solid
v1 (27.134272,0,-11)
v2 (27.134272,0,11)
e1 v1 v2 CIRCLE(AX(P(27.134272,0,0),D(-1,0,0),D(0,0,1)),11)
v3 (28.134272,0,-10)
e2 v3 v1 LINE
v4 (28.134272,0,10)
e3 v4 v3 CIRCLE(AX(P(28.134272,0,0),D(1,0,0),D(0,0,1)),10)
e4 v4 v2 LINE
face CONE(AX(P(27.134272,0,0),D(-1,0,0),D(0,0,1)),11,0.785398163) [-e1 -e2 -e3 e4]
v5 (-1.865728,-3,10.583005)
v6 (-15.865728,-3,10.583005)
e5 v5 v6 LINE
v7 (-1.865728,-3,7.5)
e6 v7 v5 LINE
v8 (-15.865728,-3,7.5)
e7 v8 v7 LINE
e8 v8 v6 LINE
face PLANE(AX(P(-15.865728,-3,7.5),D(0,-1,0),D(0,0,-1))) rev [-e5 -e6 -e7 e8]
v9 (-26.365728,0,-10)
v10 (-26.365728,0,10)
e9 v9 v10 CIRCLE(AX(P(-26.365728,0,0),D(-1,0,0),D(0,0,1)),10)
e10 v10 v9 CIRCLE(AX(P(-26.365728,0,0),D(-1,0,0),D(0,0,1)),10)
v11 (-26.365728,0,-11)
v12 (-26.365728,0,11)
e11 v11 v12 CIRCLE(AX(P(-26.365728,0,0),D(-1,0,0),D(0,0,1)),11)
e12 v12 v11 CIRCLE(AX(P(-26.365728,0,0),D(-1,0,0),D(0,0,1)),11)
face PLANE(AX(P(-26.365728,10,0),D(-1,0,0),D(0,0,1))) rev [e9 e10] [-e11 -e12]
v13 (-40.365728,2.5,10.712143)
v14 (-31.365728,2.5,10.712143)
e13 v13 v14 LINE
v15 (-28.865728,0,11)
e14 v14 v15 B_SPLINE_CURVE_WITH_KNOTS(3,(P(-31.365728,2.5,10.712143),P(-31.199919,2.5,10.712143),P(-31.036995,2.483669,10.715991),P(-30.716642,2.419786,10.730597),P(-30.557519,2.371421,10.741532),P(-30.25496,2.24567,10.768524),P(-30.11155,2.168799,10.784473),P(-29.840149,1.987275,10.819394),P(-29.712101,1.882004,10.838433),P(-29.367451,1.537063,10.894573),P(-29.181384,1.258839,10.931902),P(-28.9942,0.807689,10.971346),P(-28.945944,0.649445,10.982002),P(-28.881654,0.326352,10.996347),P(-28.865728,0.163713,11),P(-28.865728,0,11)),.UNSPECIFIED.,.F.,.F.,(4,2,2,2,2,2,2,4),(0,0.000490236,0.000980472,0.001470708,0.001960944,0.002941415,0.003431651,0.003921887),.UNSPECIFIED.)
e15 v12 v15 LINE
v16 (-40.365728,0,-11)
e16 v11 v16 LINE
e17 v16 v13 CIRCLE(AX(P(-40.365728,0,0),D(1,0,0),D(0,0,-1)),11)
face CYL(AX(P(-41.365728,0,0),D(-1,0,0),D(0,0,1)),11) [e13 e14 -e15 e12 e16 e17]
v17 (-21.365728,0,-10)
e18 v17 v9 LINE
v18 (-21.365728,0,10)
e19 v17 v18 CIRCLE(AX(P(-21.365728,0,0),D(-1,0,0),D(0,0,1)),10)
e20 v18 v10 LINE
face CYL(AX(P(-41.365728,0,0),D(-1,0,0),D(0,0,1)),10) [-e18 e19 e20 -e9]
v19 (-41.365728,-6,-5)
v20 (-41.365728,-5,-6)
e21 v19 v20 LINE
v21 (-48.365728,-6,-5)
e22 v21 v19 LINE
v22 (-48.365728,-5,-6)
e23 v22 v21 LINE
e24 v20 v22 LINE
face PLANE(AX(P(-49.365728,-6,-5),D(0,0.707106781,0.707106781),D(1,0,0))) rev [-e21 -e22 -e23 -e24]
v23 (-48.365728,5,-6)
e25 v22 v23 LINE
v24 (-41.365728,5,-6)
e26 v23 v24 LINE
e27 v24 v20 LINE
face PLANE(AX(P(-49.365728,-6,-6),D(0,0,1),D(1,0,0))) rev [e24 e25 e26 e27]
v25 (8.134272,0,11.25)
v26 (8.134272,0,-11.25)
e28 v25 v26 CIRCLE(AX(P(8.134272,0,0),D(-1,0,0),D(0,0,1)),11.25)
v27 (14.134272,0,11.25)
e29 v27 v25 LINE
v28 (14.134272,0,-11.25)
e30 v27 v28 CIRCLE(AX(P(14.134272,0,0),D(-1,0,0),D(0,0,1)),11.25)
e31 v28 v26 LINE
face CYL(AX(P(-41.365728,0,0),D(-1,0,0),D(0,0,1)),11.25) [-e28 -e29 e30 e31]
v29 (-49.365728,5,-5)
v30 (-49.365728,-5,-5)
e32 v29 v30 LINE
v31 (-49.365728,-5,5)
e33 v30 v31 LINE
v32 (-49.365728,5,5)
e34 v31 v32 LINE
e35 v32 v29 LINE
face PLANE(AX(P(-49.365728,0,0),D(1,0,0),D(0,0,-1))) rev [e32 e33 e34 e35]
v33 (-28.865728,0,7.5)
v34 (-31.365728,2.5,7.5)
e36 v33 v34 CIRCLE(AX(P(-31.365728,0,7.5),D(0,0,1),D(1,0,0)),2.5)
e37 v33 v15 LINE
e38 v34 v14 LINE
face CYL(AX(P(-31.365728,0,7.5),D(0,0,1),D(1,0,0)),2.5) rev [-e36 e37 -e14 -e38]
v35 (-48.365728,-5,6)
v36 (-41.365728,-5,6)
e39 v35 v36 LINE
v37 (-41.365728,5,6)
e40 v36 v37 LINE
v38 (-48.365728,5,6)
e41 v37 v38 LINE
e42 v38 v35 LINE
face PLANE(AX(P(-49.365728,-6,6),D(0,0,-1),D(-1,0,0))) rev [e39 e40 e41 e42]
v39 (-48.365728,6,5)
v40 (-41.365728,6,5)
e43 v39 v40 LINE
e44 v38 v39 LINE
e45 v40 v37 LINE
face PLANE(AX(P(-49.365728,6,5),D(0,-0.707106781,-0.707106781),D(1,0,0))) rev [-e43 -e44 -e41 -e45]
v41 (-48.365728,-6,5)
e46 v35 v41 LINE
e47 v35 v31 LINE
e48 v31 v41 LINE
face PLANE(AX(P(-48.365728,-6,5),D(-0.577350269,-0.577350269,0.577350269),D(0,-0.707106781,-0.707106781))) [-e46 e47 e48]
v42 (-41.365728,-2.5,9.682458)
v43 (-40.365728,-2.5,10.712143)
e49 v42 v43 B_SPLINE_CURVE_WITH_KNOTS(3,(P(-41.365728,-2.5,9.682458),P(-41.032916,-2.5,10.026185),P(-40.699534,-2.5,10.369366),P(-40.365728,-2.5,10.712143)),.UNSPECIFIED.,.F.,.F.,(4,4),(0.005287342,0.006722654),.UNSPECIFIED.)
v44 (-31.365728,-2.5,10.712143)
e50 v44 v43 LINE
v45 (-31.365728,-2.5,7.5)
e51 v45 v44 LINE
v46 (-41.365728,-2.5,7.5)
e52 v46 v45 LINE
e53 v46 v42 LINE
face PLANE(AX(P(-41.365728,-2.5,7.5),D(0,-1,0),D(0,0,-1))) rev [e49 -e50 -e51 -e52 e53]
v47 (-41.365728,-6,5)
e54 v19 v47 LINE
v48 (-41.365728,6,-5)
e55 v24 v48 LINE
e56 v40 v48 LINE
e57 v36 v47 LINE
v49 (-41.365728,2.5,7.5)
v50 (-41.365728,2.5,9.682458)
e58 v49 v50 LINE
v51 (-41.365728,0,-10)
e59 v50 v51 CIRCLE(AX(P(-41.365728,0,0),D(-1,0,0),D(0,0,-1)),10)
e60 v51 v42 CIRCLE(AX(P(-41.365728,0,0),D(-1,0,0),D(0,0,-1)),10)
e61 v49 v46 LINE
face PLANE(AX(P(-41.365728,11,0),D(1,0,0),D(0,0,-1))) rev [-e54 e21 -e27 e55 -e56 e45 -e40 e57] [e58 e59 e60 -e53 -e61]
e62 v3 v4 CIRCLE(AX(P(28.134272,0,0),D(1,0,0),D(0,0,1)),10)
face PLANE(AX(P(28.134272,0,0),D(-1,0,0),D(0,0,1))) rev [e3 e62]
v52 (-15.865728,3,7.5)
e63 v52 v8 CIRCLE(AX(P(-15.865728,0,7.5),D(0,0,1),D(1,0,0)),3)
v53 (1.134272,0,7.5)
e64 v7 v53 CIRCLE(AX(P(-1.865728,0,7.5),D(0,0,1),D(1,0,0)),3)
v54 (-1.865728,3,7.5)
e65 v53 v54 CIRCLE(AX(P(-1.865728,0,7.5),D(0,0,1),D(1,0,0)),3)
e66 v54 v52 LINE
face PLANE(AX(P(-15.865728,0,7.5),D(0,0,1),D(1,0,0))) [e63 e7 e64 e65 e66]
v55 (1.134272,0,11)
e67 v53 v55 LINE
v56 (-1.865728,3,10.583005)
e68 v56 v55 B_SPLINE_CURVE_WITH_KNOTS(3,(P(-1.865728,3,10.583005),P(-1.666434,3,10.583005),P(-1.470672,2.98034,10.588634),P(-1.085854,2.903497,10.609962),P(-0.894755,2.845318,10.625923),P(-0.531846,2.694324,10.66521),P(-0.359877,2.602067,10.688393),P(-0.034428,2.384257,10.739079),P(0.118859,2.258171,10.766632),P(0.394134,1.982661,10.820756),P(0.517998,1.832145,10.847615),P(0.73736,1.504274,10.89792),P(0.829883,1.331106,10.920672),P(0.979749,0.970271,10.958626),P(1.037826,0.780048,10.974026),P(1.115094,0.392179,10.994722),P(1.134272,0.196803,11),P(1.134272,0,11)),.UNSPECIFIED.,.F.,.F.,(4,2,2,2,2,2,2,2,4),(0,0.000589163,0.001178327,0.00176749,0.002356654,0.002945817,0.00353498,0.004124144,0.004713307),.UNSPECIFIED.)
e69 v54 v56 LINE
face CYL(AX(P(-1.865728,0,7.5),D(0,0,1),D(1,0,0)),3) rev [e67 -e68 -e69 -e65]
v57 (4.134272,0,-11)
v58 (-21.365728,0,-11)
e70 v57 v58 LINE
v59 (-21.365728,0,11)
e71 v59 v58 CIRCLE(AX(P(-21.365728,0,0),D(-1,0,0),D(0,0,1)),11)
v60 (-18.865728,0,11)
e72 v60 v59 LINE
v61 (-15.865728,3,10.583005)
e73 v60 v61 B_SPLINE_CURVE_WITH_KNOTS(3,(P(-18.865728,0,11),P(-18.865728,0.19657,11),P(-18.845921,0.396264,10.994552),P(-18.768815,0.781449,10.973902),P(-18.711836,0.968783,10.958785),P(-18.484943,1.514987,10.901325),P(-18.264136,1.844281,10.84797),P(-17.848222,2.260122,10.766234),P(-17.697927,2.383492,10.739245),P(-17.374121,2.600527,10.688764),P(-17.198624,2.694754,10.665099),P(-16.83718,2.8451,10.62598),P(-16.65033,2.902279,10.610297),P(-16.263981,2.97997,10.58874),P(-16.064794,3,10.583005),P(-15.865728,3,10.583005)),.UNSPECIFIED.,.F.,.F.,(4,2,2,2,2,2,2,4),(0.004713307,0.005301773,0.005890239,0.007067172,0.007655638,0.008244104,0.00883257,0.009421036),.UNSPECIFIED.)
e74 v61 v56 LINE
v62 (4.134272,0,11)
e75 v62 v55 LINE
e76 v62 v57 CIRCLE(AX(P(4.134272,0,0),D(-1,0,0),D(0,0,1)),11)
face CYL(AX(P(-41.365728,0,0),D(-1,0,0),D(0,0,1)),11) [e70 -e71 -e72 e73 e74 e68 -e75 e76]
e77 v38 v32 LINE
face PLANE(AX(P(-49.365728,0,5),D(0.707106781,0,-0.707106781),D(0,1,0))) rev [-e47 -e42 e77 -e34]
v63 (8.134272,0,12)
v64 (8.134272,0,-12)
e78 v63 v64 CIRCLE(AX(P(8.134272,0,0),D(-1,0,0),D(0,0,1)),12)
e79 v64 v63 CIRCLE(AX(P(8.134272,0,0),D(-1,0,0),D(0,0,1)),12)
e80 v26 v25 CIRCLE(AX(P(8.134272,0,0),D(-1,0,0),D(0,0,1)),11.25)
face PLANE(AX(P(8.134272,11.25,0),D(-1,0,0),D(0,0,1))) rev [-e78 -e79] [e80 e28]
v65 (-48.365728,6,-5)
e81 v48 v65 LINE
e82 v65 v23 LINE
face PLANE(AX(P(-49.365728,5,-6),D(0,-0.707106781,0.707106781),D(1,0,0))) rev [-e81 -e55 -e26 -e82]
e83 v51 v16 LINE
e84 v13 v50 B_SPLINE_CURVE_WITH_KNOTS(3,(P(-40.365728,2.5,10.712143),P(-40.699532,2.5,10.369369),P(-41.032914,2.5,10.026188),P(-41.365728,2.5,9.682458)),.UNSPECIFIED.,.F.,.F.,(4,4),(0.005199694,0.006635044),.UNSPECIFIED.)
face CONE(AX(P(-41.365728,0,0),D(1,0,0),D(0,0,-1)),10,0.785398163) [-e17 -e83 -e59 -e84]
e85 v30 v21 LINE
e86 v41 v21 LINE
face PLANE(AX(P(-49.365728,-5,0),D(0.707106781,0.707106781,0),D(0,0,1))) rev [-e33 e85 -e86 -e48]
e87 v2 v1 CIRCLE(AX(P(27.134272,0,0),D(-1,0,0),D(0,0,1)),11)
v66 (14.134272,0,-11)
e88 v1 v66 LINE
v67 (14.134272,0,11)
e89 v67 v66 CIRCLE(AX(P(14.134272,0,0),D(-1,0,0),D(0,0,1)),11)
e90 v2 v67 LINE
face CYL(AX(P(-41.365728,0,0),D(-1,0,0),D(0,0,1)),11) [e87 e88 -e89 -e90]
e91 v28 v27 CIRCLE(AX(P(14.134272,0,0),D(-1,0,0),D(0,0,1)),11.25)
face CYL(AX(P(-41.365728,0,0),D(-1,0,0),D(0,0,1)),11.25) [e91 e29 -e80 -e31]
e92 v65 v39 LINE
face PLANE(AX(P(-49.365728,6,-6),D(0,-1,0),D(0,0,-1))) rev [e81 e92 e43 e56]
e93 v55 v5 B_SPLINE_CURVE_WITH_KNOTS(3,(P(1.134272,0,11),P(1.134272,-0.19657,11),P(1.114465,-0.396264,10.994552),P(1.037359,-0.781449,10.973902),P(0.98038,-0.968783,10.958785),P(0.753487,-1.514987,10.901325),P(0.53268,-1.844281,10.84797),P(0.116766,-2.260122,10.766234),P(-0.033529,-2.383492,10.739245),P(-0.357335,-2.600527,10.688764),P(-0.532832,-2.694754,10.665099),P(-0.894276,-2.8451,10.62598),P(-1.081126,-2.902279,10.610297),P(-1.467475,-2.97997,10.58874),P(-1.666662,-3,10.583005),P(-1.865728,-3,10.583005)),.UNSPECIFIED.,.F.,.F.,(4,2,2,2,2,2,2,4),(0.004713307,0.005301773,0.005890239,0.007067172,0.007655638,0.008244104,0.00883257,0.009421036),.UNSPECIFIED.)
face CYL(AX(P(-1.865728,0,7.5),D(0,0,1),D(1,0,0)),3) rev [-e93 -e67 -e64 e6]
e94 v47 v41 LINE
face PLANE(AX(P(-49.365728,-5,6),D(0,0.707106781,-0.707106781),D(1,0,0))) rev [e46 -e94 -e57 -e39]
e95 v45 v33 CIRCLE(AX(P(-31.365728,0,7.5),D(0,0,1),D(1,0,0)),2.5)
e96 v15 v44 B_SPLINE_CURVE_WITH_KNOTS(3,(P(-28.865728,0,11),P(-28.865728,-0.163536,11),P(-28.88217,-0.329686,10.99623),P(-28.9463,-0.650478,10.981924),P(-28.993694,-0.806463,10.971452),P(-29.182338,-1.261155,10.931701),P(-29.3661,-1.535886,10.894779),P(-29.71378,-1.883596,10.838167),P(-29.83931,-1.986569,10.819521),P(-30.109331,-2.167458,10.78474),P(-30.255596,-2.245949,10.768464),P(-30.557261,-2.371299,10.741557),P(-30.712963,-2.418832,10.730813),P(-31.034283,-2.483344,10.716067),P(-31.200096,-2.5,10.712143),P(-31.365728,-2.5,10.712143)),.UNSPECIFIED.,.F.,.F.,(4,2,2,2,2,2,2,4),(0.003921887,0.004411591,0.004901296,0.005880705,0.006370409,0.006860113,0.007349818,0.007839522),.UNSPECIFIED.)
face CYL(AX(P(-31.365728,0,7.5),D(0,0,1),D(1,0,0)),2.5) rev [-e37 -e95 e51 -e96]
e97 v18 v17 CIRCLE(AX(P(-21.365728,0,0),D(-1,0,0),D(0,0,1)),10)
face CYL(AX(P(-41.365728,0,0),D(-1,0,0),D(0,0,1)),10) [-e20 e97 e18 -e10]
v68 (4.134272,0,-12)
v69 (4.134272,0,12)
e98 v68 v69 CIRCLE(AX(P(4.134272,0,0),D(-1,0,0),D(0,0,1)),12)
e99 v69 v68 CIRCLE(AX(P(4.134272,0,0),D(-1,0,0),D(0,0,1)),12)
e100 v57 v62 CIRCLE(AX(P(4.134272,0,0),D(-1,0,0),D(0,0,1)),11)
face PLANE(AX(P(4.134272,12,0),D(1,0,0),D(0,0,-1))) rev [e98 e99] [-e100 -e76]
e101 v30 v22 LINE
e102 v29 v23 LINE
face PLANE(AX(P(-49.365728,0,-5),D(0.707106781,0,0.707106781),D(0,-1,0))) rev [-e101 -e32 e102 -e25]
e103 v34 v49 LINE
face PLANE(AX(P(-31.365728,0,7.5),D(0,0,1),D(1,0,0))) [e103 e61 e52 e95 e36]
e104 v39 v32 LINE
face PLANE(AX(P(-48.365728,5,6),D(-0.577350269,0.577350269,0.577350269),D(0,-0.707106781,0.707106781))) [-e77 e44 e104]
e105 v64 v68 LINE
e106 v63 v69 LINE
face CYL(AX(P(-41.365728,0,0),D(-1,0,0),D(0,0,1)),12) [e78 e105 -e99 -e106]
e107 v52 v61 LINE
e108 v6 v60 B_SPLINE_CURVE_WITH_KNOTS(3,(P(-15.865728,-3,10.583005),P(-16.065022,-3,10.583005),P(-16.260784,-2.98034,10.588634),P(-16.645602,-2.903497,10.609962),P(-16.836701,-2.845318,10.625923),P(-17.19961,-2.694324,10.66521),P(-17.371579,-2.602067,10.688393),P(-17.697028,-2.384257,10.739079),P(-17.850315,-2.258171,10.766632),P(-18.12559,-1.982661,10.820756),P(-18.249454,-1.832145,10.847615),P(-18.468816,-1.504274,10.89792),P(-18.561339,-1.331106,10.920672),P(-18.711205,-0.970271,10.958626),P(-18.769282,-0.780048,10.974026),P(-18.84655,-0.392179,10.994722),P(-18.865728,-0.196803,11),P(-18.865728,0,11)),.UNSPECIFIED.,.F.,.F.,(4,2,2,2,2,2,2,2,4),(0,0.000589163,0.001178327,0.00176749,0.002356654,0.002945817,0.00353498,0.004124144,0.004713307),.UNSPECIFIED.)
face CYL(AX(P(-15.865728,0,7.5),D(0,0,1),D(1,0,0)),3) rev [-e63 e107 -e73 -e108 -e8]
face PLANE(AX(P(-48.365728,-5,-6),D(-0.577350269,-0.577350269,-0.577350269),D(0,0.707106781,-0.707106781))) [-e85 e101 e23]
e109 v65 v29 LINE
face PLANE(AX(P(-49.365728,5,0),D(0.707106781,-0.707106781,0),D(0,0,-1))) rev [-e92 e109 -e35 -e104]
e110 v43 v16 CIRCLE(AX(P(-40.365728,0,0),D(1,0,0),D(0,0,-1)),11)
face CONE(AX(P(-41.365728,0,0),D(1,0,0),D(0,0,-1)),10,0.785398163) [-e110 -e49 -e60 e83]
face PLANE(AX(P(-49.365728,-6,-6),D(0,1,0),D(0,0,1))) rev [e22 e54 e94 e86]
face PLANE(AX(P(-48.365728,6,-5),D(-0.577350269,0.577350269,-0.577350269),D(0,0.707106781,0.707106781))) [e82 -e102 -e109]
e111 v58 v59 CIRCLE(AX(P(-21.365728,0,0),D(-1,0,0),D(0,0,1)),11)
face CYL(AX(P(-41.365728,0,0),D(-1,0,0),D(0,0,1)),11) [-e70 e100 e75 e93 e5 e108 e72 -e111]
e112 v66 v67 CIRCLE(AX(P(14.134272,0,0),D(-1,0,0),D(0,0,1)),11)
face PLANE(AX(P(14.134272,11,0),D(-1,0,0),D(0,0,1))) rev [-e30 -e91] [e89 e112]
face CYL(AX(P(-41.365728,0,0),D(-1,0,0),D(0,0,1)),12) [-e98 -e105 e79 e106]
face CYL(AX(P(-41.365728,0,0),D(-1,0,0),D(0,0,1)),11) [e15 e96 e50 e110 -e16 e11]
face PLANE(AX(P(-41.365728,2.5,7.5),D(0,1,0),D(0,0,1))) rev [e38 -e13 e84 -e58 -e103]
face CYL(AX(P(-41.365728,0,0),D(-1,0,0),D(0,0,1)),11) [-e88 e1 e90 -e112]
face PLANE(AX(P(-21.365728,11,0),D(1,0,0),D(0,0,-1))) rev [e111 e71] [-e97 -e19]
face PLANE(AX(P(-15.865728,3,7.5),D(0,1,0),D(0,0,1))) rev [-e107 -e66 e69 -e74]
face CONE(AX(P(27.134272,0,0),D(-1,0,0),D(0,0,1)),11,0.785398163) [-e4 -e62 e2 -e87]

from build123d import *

# Parameters (mm, degrees)
SKETCH2_W           = 12
SKETCH2_H           = 12
BOSS_EXTRUDE1_DEPTH = 8
CHAMFER1_SIZE       = 1
CUT_EXTRUDE1_DEPTH  = 3.5
CUT_EXTRUDE2_DEPTH  = 3.5


with BuildPart() as part:
    # Sketch1 → Revolve1 (revolve)
    with BuildSketch(Plane.XY, mode=Mode.PRIVATE) as revolve1_sk:
        Polygon((-41.365727984, 0), (28.134272016, 0), (28.134272016, 11), (14.134272016, 11), (14.134272016, 11.25), (8.134272016, 11.25), (8.134272016, 12), (4.134272016, 12), (4.134272016, 11), (-21.365727984, 11), (-21.365727984, 10), (-26.365727984, 10), (-26.365727984, 11), (-41.365727984, 11), align=None)
    revolve(revolve1_sk.sketch.rotate(Axis((-41.365727984, 0, 0), (1, 0, 0)), 90), axis=Axis((-41.365727984, 0, 0), (1, 0, 0)))

    # Sketch2 → Boss-Extrude1 (add)
    with BuildSketch(Plane.ZY.offset(41.365727984)):
        Rectangle(SKETCH2_W, SKETCH2_H)
    extrude(amount=BOSS_EXTRUDE1_DEPTH)

    # Chamfer1
    chamfer1_edges = [part.edges().sort_by_distance(p)[0] for p in [
        (-41.365727984, 0, -11),
        (28.134272016, 0, -11),
        (-45.365727984, -6, 6),
        (-45.365727984, 6, 6),
        (-45.365727984, 6, -6),
        (-45.365727984, -6, -6),
        (-49.365727984, 0, 6),
        (-49.365727984, 6, 0),
        (-49.365727984, 0, -6),
        (-49.365727984, -6, 0),
    ]]
    chamfer(chamfer1_edges, length=CHAMFER1_SIZE)

    # Sketch3 → Cut-Extrude1 (cut)
    with BuildSketch(Plane.XY.offset(11)):
        with BuildLine():
            Line((-15.865727984, 3), (-1.865727984, 3))
            ThreePointArc((-1.865727984, 3), (1.134272016, 0), (-1.865727984, -3))
            Line((-1.865727984, -3), (-15.865727984, -3))
            ThreePointArc((-15.865727984, -3), (-18.865727984, 0), (-15.865727984, 3))
        make_face()
    extrude(amount=-CUT_EXTRUDE1_DEPTH, mode=Mode.SUBTRACT)

    # Sketch4 → Cut-Extrude2 (cut)
    with BuildSketch(Plane.XY.offset(11)):
        with BuildLine():
            Line((-41.365727984, -2.5), (-31.365727984, -2.5))
            ThreePointArc((-31.365727984, -2.5), (-28.865727984, 0), (-31.365727984, 2.5))
            Line((-31.365727984, 2.5), (-41.365727984, 2.5))
            Line((-41.365727984, 2.5), (-41.365727984, -2.5))
        make_face()
    extrude(amount=-CUT_EXTRUDE2_DEPTH, mode=Mode.SUBTRACT)


solid = part.part
